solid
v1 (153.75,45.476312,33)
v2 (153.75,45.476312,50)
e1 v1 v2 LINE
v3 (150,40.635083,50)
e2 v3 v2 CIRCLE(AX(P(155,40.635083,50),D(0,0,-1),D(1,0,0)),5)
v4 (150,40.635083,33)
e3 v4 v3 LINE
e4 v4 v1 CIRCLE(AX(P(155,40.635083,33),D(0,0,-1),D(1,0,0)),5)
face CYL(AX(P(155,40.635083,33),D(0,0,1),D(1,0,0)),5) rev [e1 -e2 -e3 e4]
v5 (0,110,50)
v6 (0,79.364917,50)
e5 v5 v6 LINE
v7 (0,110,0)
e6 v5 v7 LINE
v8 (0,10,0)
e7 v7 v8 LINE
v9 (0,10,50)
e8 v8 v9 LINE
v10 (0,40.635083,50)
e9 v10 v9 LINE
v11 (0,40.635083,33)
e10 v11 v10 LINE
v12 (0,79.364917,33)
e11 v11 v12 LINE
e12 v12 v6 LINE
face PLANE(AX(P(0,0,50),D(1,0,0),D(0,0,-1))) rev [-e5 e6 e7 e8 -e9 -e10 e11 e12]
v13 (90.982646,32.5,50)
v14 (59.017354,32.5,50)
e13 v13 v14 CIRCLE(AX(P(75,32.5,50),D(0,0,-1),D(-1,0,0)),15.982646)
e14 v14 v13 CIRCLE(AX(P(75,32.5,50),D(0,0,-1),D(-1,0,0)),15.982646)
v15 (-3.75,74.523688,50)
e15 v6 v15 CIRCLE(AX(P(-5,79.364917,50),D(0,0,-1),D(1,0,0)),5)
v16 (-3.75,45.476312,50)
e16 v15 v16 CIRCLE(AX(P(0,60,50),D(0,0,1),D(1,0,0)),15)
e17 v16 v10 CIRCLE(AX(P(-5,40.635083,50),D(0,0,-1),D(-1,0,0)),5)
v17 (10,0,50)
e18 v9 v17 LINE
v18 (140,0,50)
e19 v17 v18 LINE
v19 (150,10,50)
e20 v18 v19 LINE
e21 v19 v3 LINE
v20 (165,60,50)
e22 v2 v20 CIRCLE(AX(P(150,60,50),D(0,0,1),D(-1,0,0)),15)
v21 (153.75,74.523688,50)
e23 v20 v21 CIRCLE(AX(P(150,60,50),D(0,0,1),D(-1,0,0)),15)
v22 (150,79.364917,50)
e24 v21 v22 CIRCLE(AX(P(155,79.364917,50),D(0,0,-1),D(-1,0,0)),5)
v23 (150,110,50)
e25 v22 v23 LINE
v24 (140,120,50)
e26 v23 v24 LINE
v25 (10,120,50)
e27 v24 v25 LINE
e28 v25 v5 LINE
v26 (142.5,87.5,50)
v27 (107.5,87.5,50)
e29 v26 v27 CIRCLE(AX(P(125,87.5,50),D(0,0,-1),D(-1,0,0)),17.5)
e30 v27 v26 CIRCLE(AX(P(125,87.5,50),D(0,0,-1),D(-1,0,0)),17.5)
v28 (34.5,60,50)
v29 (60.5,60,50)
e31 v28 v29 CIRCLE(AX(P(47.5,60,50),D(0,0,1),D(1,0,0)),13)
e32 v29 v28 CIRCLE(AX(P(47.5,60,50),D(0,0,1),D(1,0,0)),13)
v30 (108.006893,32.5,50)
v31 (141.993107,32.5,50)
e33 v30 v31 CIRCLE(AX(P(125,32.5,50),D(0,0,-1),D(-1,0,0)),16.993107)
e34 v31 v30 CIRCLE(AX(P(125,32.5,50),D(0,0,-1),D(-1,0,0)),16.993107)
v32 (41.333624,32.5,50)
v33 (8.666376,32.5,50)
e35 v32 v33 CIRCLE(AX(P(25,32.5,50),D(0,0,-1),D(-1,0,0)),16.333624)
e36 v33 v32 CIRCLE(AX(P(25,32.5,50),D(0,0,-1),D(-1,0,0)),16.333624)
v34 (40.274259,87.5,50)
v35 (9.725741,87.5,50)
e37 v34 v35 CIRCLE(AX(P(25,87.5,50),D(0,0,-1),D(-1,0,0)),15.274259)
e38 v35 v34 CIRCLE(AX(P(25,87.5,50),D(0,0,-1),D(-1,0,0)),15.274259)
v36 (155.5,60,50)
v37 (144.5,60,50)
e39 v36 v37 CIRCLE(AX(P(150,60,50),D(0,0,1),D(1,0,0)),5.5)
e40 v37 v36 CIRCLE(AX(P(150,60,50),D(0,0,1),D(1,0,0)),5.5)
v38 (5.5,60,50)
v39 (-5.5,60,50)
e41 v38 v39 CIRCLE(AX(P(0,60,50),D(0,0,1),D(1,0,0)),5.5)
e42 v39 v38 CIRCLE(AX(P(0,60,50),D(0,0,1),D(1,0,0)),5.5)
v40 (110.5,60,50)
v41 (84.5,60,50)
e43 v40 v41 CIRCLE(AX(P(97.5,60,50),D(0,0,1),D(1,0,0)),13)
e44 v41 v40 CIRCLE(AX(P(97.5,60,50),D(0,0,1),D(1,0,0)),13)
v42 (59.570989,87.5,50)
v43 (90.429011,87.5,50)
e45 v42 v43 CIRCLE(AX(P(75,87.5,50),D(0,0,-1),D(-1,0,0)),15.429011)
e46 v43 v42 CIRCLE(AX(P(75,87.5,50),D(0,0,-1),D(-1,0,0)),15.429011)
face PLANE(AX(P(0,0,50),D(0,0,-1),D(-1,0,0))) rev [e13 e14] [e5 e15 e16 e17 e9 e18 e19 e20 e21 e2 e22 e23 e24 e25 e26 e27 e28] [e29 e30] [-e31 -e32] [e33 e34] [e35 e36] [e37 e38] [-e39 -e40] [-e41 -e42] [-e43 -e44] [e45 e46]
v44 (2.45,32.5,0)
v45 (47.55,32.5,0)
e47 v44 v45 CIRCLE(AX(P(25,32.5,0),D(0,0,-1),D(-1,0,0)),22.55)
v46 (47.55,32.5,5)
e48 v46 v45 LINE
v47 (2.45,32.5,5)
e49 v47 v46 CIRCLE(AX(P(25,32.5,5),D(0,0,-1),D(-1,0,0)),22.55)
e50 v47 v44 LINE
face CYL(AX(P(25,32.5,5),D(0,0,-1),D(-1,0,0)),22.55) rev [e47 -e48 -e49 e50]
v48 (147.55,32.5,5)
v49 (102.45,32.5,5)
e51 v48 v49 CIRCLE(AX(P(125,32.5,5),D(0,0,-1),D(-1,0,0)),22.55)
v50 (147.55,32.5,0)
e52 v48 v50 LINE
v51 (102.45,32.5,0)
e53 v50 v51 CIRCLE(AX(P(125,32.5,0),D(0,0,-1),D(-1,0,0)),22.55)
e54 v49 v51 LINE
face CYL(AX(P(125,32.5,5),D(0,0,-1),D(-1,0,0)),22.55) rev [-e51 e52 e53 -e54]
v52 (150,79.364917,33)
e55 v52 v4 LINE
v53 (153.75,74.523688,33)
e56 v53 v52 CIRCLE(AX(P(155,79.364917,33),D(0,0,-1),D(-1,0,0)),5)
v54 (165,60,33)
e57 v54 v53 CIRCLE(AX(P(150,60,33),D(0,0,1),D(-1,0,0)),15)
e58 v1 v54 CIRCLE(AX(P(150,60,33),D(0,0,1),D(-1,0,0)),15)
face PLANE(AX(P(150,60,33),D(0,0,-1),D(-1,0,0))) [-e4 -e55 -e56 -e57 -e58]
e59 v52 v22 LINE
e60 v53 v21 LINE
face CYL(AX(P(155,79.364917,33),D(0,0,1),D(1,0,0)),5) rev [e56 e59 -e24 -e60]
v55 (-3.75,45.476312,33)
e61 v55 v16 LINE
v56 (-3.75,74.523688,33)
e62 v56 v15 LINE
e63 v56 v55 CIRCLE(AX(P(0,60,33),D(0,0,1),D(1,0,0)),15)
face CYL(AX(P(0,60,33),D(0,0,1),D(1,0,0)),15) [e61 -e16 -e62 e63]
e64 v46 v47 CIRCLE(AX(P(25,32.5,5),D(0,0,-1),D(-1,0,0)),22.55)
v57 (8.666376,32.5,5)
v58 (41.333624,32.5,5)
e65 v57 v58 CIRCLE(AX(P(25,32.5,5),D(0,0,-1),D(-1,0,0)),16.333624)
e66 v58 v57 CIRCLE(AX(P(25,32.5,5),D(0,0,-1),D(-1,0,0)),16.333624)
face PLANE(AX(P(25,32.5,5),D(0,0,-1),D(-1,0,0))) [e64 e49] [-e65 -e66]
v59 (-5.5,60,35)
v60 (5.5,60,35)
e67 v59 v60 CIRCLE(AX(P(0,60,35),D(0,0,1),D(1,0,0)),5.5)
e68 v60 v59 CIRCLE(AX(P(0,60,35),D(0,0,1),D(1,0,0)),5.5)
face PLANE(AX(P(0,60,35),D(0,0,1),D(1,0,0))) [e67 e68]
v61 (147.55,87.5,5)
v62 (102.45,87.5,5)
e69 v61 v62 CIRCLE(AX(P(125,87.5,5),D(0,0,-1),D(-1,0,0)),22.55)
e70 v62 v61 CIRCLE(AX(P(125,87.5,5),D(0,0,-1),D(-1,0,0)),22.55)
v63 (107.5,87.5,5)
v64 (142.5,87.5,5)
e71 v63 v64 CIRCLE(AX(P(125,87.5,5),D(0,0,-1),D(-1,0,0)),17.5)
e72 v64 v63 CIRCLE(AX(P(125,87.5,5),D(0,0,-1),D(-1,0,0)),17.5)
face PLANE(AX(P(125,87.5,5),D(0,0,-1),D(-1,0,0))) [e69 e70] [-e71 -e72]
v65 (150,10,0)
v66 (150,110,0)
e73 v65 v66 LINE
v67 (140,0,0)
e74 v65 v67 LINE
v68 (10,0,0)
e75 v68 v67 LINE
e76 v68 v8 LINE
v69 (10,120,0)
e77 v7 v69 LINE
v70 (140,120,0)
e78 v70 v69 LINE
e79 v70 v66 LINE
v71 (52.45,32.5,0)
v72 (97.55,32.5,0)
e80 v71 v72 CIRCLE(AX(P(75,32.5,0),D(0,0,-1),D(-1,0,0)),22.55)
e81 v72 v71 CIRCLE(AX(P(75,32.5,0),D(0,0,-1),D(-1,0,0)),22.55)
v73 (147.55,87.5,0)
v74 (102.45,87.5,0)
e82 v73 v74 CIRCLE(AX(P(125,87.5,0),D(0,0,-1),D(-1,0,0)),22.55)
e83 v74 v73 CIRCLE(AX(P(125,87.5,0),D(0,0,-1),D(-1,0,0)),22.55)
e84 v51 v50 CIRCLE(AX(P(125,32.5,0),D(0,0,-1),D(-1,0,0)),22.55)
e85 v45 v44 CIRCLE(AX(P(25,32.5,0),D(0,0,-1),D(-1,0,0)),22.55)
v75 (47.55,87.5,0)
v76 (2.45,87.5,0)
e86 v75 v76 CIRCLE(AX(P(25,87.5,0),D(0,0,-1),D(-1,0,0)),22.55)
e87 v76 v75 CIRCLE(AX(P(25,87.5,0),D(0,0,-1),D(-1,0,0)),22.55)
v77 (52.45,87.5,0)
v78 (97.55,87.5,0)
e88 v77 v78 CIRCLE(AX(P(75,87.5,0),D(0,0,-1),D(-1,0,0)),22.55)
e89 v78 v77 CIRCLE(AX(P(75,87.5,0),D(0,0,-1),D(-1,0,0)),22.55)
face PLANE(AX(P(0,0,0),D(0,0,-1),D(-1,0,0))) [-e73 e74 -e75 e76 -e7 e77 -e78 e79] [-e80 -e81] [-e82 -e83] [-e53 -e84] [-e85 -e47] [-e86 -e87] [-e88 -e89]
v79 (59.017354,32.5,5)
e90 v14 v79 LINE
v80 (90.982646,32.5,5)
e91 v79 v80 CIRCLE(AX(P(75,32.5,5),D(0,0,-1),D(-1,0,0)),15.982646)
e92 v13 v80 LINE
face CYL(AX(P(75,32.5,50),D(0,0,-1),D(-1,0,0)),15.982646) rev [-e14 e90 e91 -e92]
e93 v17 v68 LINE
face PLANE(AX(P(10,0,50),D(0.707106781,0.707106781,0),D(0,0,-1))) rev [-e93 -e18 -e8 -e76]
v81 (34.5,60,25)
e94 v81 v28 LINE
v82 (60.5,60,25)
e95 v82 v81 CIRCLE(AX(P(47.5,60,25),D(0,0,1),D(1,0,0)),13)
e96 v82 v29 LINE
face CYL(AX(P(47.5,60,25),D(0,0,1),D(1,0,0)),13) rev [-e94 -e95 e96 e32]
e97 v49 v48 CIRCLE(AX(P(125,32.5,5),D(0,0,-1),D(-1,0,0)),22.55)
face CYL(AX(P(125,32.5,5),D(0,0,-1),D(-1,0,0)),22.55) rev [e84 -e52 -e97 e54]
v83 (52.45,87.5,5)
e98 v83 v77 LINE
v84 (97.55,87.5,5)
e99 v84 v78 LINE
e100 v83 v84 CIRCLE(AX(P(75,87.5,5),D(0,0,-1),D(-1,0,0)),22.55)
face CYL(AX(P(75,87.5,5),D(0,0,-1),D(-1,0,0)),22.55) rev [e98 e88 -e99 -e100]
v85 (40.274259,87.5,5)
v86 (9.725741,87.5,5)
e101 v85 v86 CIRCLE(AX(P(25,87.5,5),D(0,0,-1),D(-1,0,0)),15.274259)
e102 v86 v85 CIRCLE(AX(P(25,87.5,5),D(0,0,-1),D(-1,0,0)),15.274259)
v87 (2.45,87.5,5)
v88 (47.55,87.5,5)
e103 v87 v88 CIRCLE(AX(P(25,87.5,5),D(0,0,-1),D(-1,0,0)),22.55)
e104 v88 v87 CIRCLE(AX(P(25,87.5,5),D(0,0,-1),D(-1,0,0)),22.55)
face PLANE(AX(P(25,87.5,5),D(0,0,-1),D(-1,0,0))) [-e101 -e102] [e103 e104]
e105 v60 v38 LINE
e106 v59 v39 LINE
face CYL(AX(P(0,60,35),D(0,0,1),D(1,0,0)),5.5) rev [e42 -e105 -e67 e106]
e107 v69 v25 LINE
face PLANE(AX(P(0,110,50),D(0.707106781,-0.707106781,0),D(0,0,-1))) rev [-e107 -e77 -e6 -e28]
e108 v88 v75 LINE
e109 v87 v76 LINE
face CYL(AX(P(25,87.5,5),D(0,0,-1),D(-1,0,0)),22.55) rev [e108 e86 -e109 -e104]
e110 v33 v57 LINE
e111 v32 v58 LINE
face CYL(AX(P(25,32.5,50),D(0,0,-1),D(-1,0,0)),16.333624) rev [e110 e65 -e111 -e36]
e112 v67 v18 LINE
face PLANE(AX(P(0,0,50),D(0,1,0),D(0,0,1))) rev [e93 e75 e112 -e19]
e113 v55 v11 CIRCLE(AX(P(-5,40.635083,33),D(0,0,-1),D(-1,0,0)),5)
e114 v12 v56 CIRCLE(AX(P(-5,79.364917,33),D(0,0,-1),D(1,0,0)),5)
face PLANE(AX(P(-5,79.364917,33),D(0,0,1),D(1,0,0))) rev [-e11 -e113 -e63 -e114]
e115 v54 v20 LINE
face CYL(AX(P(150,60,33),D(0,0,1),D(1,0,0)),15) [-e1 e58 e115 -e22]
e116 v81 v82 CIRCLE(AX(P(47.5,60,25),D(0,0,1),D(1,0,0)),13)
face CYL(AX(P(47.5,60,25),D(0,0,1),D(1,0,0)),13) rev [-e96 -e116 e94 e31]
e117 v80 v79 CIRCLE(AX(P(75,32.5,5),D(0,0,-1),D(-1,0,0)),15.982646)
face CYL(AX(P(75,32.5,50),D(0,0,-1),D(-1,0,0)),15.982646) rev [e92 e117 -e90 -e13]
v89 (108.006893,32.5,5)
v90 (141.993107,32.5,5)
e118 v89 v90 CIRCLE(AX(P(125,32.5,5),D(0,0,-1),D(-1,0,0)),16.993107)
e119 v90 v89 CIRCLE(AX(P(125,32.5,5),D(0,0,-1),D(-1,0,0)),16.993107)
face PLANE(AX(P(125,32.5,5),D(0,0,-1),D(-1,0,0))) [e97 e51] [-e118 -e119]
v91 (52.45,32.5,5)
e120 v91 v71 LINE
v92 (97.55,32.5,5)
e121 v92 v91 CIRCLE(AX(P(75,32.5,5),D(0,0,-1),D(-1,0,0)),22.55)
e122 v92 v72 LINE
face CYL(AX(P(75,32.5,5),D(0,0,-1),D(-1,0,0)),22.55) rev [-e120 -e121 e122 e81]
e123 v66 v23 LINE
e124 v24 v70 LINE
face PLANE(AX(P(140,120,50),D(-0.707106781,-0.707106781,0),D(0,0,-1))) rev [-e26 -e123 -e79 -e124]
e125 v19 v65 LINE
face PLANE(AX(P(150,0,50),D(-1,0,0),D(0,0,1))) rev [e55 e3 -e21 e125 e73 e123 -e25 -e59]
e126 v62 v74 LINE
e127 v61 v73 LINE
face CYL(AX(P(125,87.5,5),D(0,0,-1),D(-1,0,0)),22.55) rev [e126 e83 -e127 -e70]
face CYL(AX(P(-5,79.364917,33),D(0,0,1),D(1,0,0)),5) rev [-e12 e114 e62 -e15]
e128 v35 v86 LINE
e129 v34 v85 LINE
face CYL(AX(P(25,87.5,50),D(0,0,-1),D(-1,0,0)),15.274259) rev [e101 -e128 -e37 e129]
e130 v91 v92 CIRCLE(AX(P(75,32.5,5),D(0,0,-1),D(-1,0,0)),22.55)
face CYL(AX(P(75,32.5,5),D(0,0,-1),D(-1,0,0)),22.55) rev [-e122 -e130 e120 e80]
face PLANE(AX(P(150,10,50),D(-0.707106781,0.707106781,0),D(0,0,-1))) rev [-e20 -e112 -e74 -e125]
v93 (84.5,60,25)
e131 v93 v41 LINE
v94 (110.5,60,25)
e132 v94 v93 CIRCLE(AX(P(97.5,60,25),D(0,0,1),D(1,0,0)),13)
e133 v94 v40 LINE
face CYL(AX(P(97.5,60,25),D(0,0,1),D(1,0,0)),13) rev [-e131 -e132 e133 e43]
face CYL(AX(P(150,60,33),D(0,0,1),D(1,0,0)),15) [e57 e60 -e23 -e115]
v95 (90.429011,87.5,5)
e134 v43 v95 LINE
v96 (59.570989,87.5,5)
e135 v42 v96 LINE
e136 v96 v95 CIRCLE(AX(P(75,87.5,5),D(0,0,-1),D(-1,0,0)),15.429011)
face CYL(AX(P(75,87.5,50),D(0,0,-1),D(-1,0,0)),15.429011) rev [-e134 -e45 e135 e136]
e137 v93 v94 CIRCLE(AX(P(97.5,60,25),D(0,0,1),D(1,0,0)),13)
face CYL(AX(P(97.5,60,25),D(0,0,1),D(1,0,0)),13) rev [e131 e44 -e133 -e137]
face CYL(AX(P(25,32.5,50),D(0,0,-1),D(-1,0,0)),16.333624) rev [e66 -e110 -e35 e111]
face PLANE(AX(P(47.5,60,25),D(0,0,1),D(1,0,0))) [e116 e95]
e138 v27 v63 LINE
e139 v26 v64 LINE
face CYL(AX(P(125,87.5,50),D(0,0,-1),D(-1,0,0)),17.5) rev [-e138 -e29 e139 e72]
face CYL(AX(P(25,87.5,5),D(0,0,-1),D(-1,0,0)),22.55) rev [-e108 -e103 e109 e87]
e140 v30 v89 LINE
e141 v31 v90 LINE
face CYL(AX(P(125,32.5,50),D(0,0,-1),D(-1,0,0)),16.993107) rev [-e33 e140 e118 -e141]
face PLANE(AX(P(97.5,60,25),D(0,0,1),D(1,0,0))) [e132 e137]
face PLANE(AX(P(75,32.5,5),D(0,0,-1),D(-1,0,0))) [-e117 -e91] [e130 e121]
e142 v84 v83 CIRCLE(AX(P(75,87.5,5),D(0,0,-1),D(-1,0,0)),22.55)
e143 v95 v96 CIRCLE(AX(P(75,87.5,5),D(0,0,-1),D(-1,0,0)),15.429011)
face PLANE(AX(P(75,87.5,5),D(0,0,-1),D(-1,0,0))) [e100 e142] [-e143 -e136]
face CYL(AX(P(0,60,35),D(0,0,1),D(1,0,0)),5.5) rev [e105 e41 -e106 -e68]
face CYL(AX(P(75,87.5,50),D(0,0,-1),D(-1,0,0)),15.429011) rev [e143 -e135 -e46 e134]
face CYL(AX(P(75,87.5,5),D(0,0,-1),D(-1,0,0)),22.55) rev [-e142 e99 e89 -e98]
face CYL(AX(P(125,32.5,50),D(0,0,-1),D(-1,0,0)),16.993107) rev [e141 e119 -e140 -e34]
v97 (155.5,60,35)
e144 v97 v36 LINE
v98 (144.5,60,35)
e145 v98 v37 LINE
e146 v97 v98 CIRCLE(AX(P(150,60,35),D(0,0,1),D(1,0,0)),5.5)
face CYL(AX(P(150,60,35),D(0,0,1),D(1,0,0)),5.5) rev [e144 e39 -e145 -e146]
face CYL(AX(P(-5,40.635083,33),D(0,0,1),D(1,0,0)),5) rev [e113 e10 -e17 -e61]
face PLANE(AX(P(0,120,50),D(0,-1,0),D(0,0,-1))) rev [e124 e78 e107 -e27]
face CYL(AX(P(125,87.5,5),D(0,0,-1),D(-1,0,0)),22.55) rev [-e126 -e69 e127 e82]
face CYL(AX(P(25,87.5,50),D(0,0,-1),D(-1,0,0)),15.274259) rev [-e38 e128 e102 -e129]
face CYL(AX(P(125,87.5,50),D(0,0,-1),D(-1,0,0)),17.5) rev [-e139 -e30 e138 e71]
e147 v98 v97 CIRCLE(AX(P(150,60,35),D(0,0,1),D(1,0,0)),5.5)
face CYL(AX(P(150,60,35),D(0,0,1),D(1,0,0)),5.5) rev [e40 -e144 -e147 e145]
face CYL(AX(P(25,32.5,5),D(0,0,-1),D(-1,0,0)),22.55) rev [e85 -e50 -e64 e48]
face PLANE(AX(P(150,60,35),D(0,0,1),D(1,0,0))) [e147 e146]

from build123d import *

# Parameters (mm, degrees)
BLOCK_PROFILE_SKETCH_W         = 150
BLOCK_PROFILE_SKETCH_H         = 120
BASE_BLOCK_150X120X50_DEPTH    = 50
PORT_COUNTERBORE_SKETCH_R      = 22.55
PORT_COUNTERBORES_5_DEEP_DEPTH = 5
PORT_HOLE_SKETCH_R             = 17.5
PORT_HOLE_SKETCH_R_2           = 15.429011377
PORT_HOLE_SKETCH_R_3           = 15.274258873
PORT_HOLE_SKETCH_R_4           = 16.993106502
PORT_HOLE_SKETCH_R_5           = 15.982646342
PORT_HOLE_SKETCH_R_6           = 16.333623566
PORT_THROUGH_HOLES_DEPTH       = 198.294196569
EDGE_CHAMFER_10X45_A_SIZE      = 10
EDGE_CHAMFER_10X45_B_SIZE      = 10
MOUNTING_EARS_DEPTH            = 17
EAR_HOLE_SKETCH_R              = 5.5
EAR_HOLES_DEPTH                = 15
SIDE_RECESS_SKETCH_R           = 13
SIDE_RECESS_DEPTH              = 25


with BuildPart() as part:
    # Block Profile Sketch → Base Block 150x120x50 (new body)
    with BuildSketch(Plane.XY):
        with Locations((75, 60)):
            Rectangle(BLOCK_PROFILE_SKETCH_W, BLOCK_PROFILE_SKETCH_H)
    extrude(amount=BASE_BLOCK_150X120X50_DEPTH)

    # Port Counterbore Sketch → Port Counterbores 5 Deep (cut)
    with BuildSketch(Plane(origin=(0, 0, 0), x_dir=(-1, 0, 0), z_dir=(0, 0, -1))):
        with Locations((-125, 87.5)):
            Circle(PORT_COUNTERBORE_SKETCH_R)
        with Locations((-75, 87.5)):
            Circle(PORT_COUNTERBORE_SKETCH_R)
        with Locations((-25, 87.5)):
            Circle(PORT_COUNTERBORE_SKETCH_R)
        with Locations((-25, 32.5)):
            Circle(PORT_COUNTERBORE_SKETCH_R)
        with Locations((-75, 32.5)):
            Circle(PORT_COUNTERBORE_SKETCH_R)
        with Locations((-125, 32.5)):
            Circle(PORT_COUNTERBORE_SKETCH_R)
    extrude(amount=-PORT_COUNTERBORES_5_DEEP_DEPTH, mode=Mode.SUBTRACT)

    # Port Hole Sketch → Port Through Holes (cut, through all)
    with BuildSketch(Plane(origin=(0, 0, 5), x_dir=(-1, 0, 0), z_dir=(0, 0, -1))):
        with Locations((-125, 87.5)):
            Circle(PORT_HOLE_SKETCH_R)
        with Locations((-75, 87.5)):
            Circle(PORT_HOLE_SKETCH_R_2)
        with Locations((-25, 87.5)):
            Circle(PORT_HOLE_SKETCH_R_3)
        with Locations((-125, 32.5)):
            Circle(PORT_HOLE_SKETCH_R_4)
        with Locations((-75, 32.5)):
            Circle(PORT_HOLE_SKETCH_R_5)
        with Locations((-25, 32.5)):
            Circle(PORT_HOLE_SKETCH_R_6)
    extrude(amount=-PORT_THROUGH_HOLES_DEPTH, mode=Mode.SUBTRACT)

    # Edge Chamfer 10x45 A
    edge_chamfer_10x45_a_edges = [part.edges().sort_by_distance(p)[0] for p in [
        (0, 0, 25),
    ]]
    chamfer(edge_chamfer_10x45_a_edges, length=EDGE_CHAMFER_10X45_A_SIZE)

    # Edge Chamfer 10x45 B
    edge_chamfer_10x45_b_edges = [part.edges().sort_by_distance(p)[0] for p in [
        (0, 120, 25),
        (150, 120, 25),
        (150, 0, 25),
    ]]
    chamfer(edge_chamfer_10x45_b_edges, length=EDGE_CHAMFER_10X45_B_SIZE)

    # Mounting Ear Profile Sketch → Mounting Ears (add)
    with BuildSketch(Plane.XY.offset(50)):
        with BuildLine():
            Line((0, 79.364916731), (0, 40.635083269))
            ThreePointArc((0, 40.635083269), (-1.047152925, 43.696945447), (-3.75, 45.476312452))
            ThreePointArc((-3.75, 45.476312452), (-15, 60), (-3.75, 74.523687548))
            ThreePointArc((-3.75, 74.523687548), (-1.047152925, 76.303054553), (0, 79.364916731))
        make_face()
        with BuildLine():
            Line((150, 79.364916731), (150, 40.635083269))
            ThreePointArc((150, 40.635083269), (151.047152925, 43.696945447), (153.75, 45.476312452))
            ThreePointArc((153.75, 45.476312452), (165, 60), (153.75, 74.523687548))
            ThreePointArc((153.75, 74.523687548), (151.047152925, 76.303054553), (150, 79.364916731))
        make_face()
    extrude(amount=-MOUNTING_EARS_DEPTH)

    # Ear Hole Sketch → Ear Holes (cut)
    with BuildSketch(Plane.XY.offset(50)):
        with Locations((150, 60)):
            Circle(EAR_HOLE_SKETCH_R)
        with Locations((0, 60)):
            Circle(EAR_HOLE_SKETCH_R)
    extrude(amount=-EAR_HOLES_DEPTH, mode=Mode.SUBTRACT)

    # Side Recess Sketch → Side Recess (cut)
    with BuildSketch(Plane.XY.offset(50)):
        with Locations((47.5, 60)):
            Circle(SIDE_RECESS_SKETCH_R)
        with Locations((97.5, 60)):
            Circle(SIDE_RECESS_SKETCH_R)
    extrude(amount=-SIDE_RECESS_DEPTH, mode=Mode.SUBTRACT)


solid = part.part
